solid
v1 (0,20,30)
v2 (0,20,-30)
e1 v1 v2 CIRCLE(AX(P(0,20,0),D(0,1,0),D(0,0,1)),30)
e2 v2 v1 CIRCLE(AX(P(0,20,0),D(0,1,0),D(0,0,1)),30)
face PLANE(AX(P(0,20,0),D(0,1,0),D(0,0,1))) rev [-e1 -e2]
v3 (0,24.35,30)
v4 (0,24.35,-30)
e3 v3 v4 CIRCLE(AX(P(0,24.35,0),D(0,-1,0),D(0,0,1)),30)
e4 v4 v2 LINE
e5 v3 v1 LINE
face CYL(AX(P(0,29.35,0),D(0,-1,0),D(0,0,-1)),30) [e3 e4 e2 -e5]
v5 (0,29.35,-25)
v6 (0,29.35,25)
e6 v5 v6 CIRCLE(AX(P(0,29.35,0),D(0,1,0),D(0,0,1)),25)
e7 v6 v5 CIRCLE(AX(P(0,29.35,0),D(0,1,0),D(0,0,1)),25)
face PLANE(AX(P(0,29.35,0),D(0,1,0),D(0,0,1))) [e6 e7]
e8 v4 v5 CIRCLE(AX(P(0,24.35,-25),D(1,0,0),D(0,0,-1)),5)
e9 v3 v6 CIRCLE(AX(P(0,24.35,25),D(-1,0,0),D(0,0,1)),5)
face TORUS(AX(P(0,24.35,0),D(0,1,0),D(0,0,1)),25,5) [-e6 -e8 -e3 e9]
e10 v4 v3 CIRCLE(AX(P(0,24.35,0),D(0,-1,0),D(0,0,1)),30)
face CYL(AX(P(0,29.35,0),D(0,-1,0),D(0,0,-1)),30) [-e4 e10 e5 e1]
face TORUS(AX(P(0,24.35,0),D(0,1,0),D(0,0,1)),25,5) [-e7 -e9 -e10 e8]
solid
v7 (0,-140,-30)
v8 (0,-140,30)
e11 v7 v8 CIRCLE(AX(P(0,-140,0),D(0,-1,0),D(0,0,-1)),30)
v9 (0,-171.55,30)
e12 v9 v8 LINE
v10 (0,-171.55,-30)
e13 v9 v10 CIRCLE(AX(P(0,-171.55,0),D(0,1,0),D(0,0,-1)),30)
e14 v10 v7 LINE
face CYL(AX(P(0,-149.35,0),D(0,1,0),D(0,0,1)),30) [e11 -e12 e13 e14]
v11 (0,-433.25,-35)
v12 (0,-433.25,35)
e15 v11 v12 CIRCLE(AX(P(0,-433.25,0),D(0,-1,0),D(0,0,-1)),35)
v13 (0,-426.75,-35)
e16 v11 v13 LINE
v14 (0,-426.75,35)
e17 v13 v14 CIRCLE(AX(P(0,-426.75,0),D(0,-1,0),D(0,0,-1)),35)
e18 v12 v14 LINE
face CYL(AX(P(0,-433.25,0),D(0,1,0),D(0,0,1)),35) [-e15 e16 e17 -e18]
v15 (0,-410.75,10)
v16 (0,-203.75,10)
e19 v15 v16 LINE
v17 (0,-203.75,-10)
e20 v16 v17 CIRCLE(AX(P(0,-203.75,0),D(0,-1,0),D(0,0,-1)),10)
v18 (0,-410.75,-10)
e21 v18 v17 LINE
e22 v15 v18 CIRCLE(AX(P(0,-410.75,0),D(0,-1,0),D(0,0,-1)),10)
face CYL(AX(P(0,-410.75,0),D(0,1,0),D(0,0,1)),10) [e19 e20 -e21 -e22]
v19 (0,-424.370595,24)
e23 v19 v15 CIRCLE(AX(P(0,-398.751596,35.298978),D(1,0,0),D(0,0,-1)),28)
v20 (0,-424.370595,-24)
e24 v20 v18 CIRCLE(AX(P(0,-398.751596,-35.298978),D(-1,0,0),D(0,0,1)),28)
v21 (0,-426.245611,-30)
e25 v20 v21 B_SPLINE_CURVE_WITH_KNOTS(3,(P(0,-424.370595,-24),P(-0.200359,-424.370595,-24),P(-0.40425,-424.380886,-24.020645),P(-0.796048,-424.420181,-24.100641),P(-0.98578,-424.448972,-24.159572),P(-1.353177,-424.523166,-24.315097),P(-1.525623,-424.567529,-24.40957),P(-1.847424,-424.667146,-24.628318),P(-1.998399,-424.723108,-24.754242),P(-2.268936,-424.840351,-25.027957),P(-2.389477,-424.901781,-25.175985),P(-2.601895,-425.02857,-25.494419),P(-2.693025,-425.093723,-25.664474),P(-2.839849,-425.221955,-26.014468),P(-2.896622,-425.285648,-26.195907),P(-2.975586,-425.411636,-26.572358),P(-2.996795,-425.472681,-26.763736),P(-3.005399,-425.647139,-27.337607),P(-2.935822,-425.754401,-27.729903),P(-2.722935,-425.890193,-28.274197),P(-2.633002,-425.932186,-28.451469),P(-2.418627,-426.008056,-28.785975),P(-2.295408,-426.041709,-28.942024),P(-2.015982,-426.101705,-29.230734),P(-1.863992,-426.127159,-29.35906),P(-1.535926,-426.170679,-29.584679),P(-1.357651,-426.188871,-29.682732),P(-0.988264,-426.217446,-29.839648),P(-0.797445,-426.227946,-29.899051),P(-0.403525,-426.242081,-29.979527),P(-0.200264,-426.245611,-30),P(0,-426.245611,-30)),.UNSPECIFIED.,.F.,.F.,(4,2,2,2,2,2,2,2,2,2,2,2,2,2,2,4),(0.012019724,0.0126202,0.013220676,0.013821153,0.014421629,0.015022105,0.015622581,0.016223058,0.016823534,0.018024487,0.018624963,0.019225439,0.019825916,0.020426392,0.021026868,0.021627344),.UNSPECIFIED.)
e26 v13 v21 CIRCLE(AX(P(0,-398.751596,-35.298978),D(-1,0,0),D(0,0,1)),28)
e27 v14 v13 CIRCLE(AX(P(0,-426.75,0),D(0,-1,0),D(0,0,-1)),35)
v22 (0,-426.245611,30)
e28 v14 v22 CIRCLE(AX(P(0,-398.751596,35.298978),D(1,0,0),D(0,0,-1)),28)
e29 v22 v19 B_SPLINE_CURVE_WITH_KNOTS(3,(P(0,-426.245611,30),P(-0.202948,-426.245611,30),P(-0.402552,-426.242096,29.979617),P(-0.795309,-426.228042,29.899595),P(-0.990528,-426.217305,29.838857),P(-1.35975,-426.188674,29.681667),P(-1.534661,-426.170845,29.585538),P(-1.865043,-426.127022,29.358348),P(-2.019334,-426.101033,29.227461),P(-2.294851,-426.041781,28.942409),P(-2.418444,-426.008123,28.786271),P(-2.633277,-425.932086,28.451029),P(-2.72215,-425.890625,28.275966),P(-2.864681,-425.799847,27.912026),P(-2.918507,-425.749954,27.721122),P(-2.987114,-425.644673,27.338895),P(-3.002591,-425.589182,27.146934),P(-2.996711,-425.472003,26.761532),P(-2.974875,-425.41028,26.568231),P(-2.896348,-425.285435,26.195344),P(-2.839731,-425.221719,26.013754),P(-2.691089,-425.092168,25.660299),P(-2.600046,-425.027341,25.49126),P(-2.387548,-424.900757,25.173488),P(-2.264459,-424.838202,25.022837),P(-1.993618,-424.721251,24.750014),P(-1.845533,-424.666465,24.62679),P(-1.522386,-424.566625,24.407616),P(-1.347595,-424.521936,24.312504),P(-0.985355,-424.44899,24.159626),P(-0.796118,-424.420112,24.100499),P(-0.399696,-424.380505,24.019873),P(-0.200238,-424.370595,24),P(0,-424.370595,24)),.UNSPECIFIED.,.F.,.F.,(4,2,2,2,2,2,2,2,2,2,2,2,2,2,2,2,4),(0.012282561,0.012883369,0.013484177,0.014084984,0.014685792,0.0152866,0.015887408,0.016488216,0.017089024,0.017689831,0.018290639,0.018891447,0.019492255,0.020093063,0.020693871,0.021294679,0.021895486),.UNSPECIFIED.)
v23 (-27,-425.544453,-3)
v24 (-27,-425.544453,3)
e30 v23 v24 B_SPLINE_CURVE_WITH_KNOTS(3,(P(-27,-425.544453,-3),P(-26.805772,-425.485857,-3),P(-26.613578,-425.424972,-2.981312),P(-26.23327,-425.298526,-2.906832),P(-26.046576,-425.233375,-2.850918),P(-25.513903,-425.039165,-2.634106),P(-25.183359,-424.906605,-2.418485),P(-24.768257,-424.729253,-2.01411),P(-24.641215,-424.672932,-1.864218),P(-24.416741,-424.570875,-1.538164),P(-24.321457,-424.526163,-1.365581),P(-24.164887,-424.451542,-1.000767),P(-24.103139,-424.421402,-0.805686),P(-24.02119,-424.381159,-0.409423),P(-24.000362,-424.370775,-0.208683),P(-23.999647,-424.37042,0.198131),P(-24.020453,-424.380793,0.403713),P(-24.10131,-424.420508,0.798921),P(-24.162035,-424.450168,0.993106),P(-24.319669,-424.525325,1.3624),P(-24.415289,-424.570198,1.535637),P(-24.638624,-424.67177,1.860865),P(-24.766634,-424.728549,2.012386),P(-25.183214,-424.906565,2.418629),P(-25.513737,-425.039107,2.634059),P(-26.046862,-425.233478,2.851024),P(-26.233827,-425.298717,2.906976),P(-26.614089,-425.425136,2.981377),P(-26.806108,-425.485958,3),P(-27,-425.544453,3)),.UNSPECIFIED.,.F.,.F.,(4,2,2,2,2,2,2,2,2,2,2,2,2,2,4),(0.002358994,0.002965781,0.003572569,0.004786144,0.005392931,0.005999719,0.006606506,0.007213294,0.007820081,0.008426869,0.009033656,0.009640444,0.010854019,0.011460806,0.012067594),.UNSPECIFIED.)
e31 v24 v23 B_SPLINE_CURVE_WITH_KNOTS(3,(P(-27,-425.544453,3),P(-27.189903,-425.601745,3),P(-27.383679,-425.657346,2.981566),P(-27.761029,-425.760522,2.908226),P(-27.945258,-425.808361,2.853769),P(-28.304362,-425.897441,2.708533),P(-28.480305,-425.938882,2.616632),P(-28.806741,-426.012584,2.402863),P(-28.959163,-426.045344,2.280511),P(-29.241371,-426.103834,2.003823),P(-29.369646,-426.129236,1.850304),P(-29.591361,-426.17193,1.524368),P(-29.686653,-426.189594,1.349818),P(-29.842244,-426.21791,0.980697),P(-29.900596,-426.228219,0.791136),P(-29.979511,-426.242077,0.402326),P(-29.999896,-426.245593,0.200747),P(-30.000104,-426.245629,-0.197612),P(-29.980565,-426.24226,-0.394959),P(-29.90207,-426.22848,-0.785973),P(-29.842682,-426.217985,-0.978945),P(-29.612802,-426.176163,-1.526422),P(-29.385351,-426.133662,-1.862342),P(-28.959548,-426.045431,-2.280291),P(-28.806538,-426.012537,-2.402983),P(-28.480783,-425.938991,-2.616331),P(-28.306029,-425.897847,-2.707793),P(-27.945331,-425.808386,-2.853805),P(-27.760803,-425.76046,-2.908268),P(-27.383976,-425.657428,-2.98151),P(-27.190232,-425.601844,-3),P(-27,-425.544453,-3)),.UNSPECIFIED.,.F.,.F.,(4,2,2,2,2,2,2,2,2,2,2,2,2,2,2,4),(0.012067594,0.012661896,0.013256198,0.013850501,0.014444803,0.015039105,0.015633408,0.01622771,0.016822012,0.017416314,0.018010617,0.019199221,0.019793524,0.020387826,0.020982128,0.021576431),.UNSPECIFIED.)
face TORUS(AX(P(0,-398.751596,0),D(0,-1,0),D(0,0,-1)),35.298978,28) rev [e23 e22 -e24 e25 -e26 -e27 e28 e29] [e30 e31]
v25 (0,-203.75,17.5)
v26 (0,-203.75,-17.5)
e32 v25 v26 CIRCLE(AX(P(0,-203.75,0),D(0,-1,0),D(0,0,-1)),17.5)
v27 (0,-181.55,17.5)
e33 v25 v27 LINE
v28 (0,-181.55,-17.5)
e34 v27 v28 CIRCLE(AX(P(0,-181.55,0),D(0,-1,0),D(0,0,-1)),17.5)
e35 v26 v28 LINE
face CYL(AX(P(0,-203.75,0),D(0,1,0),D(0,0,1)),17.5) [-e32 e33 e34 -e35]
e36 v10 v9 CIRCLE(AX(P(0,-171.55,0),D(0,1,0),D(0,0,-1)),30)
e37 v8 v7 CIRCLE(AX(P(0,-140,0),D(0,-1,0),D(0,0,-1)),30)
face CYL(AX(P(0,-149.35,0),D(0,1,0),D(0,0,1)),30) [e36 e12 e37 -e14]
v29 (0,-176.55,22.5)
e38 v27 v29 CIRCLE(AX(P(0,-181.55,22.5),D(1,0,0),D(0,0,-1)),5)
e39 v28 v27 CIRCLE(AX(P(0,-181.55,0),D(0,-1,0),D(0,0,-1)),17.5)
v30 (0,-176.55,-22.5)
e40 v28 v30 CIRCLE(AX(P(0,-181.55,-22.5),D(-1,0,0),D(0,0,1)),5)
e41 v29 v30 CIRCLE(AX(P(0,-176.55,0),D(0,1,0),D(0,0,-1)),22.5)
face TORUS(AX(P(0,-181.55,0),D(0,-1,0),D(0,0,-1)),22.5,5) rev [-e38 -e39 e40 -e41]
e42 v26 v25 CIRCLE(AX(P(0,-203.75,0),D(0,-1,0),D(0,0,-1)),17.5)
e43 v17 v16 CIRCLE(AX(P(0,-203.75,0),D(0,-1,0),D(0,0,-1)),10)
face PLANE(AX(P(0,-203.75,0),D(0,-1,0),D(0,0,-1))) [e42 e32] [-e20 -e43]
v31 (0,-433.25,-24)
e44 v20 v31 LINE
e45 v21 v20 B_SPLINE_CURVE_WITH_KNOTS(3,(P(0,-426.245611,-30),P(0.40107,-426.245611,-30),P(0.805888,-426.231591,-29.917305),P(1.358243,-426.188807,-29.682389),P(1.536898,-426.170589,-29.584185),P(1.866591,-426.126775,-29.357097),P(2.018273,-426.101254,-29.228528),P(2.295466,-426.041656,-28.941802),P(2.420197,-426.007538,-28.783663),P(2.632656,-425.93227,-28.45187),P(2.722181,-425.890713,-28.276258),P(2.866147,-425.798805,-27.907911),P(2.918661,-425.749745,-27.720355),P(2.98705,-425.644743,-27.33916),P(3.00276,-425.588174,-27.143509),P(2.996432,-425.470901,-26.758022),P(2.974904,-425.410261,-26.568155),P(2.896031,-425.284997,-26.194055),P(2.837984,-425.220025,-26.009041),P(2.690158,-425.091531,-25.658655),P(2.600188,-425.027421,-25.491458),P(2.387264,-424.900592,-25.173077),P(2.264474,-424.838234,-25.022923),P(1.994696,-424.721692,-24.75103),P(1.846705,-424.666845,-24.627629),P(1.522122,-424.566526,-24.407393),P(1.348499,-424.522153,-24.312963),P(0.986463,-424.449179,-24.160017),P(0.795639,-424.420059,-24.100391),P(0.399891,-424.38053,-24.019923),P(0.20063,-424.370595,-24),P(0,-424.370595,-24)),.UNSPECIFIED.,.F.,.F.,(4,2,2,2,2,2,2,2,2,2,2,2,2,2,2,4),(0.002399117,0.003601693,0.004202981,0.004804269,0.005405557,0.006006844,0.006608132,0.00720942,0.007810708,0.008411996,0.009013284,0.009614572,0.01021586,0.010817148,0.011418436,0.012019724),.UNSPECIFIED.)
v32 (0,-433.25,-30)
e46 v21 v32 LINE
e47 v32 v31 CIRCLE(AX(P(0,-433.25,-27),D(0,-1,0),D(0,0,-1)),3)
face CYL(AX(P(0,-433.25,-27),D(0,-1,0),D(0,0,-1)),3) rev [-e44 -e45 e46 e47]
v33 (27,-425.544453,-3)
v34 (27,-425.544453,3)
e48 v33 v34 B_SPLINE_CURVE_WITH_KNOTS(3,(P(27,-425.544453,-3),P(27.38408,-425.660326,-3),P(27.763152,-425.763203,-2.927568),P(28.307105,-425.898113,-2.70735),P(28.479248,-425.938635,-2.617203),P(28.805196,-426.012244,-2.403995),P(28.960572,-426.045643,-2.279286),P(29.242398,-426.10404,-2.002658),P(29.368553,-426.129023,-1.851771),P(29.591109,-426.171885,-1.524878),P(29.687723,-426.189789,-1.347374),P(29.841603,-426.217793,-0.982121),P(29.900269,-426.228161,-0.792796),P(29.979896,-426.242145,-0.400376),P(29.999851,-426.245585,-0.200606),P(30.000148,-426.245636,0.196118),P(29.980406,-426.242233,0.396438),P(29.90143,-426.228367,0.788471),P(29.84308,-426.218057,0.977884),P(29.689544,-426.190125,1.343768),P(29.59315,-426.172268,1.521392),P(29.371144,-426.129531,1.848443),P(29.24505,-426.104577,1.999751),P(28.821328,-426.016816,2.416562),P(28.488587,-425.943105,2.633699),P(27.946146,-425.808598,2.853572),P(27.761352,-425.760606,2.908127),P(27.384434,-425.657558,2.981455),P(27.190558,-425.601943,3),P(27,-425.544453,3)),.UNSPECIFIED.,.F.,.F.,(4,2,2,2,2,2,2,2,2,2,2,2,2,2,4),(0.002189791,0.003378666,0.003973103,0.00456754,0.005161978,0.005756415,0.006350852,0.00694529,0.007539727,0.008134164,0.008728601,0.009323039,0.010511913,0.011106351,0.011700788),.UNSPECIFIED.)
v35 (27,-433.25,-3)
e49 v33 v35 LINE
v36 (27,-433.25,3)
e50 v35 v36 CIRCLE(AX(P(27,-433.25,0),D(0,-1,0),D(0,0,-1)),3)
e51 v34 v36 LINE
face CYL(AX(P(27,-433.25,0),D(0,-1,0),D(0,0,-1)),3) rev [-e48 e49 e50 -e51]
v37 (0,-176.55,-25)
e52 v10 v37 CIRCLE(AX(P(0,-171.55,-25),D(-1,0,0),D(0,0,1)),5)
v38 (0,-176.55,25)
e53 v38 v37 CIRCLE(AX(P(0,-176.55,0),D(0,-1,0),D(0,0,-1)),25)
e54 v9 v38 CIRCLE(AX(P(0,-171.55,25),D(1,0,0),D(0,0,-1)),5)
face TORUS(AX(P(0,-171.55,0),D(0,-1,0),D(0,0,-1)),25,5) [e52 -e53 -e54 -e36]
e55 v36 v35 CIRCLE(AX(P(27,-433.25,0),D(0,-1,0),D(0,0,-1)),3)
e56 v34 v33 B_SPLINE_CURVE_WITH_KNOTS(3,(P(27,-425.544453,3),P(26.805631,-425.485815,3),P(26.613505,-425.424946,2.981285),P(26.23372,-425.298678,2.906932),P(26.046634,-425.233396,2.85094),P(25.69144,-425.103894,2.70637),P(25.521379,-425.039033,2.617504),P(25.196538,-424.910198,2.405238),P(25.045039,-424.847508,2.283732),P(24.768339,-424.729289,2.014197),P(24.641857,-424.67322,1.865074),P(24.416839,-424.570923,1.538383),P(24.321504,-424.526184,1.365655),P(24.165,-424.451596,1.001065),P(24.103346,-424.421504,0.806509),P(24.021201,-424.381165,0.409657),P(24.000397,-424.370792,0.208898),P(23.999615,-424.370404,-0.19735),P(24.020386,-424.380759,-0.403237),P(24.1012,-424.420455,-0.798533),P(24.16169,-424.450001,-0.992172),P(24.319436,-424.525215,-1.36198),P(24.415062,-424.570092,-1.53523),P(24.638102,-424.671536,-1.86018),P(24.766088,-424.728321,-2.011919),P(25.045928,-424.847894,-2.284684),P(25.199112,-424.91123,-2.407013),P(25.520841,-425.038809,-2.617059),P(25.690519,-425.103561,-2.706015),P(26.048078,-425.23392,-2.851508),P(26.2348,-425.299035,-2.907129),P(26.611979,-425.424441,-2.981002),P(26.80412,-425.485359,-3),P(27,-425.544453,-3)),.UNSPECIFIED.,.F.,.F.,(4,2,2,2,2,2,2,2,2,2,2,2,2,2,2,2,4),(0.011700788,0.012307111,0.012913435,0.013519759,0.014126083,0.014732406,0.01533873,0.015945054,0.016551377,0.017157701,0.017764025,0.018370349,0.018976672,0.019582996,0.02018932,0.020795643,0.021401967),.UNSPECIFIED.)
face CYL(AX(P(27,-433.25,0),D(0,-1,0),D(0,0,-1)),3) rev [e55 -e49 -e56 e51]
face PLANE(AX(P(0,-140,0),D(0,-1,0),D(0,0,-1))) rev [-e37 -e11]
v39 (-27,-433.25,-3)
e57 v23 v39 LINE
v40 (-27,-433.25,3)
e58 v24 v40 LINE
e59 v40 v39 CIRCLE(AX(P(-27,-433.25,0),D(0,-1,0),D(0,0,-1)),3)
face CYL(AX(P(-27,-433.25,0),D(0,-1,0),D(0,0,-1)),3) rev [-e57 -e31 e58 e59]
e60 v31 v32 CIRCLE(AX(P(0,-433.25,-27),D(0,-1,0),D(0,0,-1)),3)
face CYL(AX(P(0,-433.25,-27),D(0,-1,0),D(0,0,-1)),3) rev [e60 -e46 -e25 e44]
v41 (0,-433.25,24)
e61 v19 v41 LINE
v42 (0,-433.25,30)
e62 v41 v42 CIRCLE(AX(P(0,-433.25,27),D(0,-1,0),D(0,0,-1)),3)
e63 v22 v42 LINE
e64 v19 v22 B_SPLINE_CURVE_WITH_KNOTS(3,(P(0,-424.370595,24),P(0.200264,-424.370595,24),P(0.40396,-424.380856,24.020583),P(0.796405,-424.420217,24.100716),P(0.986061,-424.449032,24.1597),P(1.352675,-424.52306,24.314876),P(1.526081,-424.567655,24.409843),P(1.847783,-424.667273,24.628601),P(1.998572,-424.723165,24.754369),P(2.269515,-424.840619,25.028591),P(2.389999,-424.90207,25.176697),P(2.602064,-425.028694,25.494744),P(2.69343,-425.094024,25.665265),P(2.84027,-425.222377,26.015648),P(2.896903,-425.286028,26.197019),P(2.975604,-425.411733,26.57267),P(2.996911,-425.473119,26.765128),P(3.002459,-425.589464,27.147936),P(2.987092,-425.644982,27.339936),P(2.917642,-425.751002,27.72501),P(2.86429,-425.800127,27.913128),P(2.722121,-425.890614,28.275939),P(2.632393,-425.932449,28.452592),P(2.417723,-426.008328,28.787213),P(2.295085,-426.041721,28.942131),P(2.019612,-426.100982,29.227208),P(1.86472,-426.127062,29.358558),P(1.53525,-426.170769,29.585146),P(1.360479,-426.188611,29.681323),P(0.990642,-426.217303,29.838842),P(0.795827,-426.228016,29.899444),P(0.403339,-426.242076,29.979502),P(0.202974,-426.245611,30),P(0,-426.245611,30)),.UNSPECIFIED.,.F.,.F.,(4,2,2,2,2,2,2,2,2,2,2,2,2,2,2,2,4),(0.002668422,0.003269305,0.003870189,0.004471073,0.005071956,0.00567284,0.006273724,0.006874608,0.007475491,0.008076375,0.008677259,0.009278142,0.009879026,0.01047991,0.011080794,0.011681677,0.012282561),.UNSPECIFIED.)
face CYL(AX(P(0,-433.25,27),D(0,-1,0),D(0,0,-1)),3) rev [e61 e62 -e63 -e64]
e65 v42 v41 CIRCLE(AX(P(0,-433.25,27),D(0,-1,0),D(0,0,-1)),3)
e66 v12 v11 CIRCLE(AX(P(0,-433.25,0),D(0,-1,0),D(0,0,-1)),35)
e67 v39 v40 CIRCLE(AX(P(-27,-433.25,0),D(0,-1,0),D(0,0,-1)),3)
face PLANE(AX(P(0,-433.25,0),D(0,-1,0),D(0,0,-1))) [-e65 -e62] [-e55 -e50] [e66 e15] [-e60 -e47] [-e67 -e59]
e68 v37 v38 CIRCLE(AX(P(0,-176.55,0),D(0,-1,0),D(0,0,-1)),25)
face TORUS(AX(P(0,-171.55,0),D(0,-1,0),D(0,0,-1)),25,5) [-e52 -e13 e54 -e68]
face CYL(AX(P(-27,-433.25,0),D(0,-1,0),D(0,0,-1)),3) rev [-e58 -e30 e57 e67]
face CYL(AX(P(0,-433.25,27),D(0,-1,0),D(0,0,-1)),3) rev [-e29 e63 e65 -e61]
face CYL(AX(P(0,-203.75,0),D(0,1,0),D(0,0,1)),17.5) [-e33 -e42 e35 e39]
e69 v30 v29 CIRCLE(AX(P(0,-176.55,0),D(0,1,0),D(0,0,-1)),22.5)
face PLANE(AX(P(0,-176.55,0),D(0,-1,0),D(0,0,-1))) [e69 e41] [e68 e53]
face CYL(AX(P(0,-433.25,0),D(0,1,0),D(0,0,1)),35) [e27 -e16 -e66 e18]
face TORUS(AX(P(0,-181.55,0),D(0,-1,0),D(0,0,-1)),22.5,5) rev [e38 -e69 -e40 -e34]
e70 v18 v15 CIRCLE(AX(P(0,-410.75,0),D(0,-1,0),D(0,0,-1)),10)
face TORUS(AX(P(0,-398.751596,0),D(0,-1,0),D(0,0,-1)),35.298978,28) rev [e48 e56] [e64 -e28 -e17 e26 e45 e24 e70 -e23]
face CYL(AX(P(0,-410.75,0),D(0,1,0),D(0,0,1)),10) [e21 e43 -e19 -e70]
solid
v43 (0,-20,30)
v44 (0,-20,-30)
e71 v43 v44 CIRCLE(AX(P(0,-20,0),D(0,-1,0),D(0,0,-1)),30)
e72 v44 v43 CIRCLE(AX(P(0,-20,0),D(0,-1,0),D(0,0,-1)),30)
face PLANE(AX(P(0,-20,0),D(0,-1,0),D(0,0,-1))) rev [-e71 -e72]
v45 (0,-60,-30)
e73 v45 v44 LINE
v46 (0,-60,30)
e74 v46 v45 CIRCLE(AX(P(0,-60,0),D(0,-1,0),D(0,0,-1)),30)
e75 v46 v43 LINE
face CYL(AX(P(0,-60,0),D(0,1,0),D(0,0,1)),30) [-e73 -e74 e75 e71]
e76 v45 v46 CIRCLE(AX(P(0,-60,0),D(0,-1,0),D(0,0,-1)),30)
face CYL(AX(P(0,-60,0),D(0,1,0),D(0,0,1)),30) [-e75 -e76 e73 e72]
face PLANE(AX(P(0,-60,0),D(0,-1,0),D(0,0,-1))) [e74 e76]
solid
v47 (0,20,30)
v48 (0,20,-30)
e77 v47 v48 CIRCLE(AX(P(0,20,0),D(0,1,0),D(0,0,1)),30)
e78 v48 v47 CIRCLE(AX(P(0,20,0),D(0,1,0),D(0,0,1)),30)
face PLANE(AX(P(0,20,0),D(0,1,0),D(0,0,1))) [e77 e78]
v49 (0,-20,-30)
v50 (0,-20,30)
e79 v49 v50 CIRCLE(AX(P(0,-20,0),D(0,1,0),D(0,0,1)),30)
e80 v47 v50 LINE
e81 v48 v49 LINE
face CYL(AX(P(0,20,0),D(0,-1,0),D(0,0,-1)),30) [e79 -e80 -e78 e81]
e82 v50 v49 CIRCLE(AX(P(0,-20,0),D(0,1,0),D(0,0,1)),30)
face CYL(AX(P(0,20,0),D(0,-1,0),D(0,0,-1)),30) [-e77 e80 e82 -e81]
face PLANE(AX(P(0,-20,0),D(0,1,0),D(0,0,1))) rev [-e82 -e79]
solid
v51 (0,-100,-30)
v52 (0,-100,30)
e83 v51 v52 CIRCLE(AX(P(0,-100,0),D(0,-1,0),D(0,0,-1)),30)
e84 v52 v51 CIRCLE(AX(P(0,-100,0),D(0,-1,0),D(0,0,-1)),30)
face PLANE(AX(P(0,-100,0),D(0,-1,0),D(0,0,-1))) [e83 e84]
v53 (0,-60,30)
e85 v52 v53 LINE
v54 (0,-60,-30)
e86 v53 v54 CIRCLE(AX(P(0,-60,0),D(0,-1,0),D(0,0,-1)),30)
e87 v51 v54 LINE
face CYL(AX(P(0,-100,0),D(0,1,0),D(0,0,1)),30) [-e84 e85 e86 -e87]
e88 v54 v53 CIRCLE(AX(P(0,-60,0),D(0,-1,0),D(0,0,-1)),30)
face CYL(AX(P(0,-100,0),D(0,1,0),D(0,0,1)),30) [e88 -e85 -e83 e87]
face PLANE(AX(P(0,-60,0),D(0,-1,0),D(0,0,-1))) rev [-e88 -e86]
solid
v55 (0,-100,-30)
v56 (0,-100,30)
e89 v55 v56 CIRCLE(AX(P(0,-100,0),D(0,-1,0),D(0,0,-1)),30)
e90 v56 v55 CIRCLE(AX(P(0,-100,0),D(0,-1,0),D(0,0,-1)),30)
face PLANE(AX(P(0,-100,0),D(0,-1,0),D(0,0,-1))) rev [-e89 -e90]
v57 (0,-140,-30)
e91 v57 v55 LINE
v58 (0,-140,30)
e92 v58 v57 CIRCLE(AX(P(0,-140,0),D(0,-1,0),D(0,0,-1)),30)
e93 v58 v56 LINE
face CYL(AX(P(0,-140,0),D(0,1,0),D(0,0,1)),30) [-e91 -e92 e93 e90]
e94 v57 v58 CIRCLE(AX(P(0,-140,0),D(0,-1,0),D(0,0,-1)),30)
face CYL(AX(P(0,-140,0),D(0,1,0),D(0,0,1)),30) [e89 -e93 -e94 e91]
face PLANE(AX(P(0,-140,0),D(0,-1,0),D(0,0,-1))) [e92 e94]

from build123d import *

# Parameters (mm, degrees)
SKETCH_1_R                     = 30
EXTRUDE_1_DEPTH                = 20
SKETCH_2_R                     = 30
EXTRUDE_2_DEPTH                = 40
SKETCH_3_R                     = 30
EXTRUDE_3_DEPTH                = 40
SKETCH_4_R                     = 30
EXTRUDE_4_DEPTH                = 40
SKETCH_5_R                     = 30
EXTRUDE_5_DEPTH                = 9.35
SKETCH_6_R                     = 30
EXTRUDE_6_DEPTH                = 9.35
SKETCH_7_R                     = 30
EXTRUDE_7_DEPTH                = 27.2
SKETCH_8_R                     = 17.5
EXTRUDE_8_DEPTH                = 27.2
FILLET_1_R                     = 5
SKETCH_9_R                     = 10
EXTRUDE_9_DEPTH                = 207
FILLET_2_R                     = 5
FILLET_3_R                     = 5
SKETCH_10_R                    = 35
EXTRUDE_10_DEPTH               = 22.5
HOLE_WIZARD_6_0_6_2_AT_2_COUNT = 2
HOLE_WIZARD_6_0_6_2_AT_2_PITCH = 54
HOLE_WIZARD_6_0_6_2_AT_3_COUNT = 2
HOLE_WIZARD_6_0_6_2_AT_3_PITCH = 38.183766184
HOLE_WIZARD_6_0_6_2_AT_4_COUNT = 2
HOLE_WIZARD_6_0_6_2_AT_4_PITCH = 38.183766184


with BuildPart() as part:
    # 草图1 → 凸台-拉伸1 (new, symmetric)
    with BuildSketch(Plane(origin=(0, 0, 0), x_dir=(1, 0, 0), z_dir=(0, 1, 0))):
        with Locations(Location((0, 0, 0), (0, 0, 270))):
            Circle(SKETCH_1_R)
    extrude(amount=EXTRUDE_1_DEPTH, both=True)


with BuildPart() as body_2:
    # 草图2 → 凸台-拉伸2 (new body)
    with BuildSketch(Plane.XZ.offset(20)):
        with Locations(Location((0, 0, 0), (0, 0, 270))):
            Circle(SKETCH_2_R)
    extrude(amount=EXTRUDE_2_DEPTH)


with BuildPart() as body_3:
    # 草图3 → 凸台-拉伸3 (new body)
    with BuildSketch(Plane.XZ.offset(60)):
        with Locations(Location((0, 0, 0), (0, 0, 270))):
            Circle(SKETCH_3_R)
    extrude(amount=EXTRUDE_3_DEPTH)


with BuildPart() as body_4:
    # 草图4 → 凸台-拉伸4 (new body)
    with BuildSketch(Plane.XZ.offset(100)):
        with Locations(Location((0, 0, 0), (0, 0, 270))):
            Circle(SKETCH_4_R)
    extrude(amount=EXTRUDE_4_DEPTH)


with BuildPart() as body_5:
    # 草图5 → 凸台-拉伸5 (new body)
    with BuildSketch(Plane(origin=(0, 20, 0), x_dir=(1, 0, 0), z_dir=(0, 1, 0))):
        with Locations(Location((0, 0, 0), (0, 0, 270))):
            Circle(SKETCH_5_R)
    extrude(amount=EXTRUDE_5_DEPTH)

    # 圆角1
    fillet_1_edges = [body_5.edges().sort_by_distance(p)[0] for p in [
        (0, 29.35, -30),
    ]]
    fillet(fillet_1_edges, radius=FILLET_1_R)


with BuildPart() as body_6:
    # 草图6 → 凸台-拉伸6 (new body)
    with BuildSketch(Plane.XZ.offset(140)):
        with Locations(Location((0, 0, 0), (0, 0, 270))):
            Circle(SKETCH_6_R)
    extrude(amount=EXTRUDE_6_DEPTH)

    # 草图7 → 凸台-拉伸7 (add)
    with BuildSketch(Plane.XZ.offset(149.35)):
        with Locations(Location((0, 0, 0), (0, 0, 270))):
            Circle(SKETCH_7_R)
    extrude(amount=EXTRUDE_7_DEPTH)

    # 草图8 → 凸台-拉伸8 (add)
    with BuildSketch(Plane.XZ.offset(176.55)):
        with Locations(Location((0, 0, 0), (0, 0, 270))):
            Circle(SKETCH_8_R)
    extrude(amount=EXTRUDE_8_DEPTH)

    # 草图9 → 凸台-拉伸9 (add)
    with BuildSketch(Plane.XZ.offset(203.75)):
        with Locations(Location((0, 0, 0), (0, 0, 270))):
            Circle(SKETCH_9_R)
    extrude(amount=EXTRUDE_9_DEPTH)

    # 圆角2
    fillet_2_edges = [body_6.edges().sort_by_distance(p)[0] for p in [
        (0, -176.55, 17.5),
    ]]
    fillet(fillet_2_edges, radius=FILLET_2_R)

    # 圆角3
    fillet_3_edges = [body_6.edges().sort_by_distance(p)[0] for p in [
        (0, -176.55, 30),
    ]]
    fillet(fillet_3_edges, radius=FILLET_3_R)

    # 草图10 → 凸台-拉伸10 (add)
    with BuildSketch(Plane.XZ.offset(410.75)):
        with Locations(Location((0, 0, 0), (0, 0, 90))):
            Circle(SKETCH_10_R)
    extrude(amount=EXTRUDE_10_DEPTH)

    # 草图11 → 切除-旋转1 (revolve, cut)
    with BuildSketch(Plane(origin=(0, 0, 0), x_dir=(0, 0, -1), z_dir=(1, 0, 0))):
        with BuildLine():
            Line((10, -410.75), (35, -410.75))
            Line((35, -410.75), (35, -426.75))
            ThreePointArc((35, -426.75), (20.205474893, -422.33519548), (10, -410.75))
        make_face()
    revolve(axis=Axis((0, -433.25, 0), (0, 1, 0)), mode=Mode.SUBTRACT)

    # 草图15 → Ø6.0 (6) 直径孔2 (revolve, cut)
    with BuildSketch(Plane(origin=(0, -433.25, 27), x_dir=(0, 0, -1), z_dir=(1, 0, 0))):
        Polygon((0, 0), (0, 36.802581857), (3, 35), (3, 0), align=None)
    hole_wizard_6_0_6_2 = revolve(axis=Axis((0, -439.6, 27), (0, 1, 0)), mode=Mode.SUBTRACT)

    # Ø6.0 (6) 直径孔2 at 2: Ø6.0 (6) 直径孔2 ×2
    with Locations(*[(0, 0, -i * HOLE_WIZARD_6_0_6_2_AT_2_PITCH) for i in range(1, HOLE_WIZARD_6_0_6_2_AT_2_COUNT)]):
        add(hole_wizard_6_0_6_2, mode=Mode.SUBTRACT)

    # Ø6.0 (6) 直径孔2 at 3: Ø6.0 (6) 直径孔2 ×2
    with Locations(*[Vector(-0.7071067811865476, 0, -0.7071067811865476) * (i * HOLE_WIZARD_6_0_6_2_AT_3_PITCH) for i in range(1, HOLE_WIZARD_6_0_6_2_AT_3_COUNT)]):
        add(hole_wizard_6_0_6_2, mode=Mode.SUBTRACT)

    # Ø6.0 (6) 直径孔2 at 4: Ø6.0 (6) 直径孔2 ×2
    with Locations(*[Vector(0.7071067811865476, 0, -0.7071067811865476) * (i * HOLE_WIZARD_6_0_6_2_AT_4_PITCH) for i in range(1, HOLE_WIZARD_6_0_6_2_AT_4_COUNT)]):
        add(hole_wizard_6_0_6_2, mode=Mode.SUBTRACT)


solid = Compound([part.part, body_2.part, body_3.part, body_4.part, body_5.part, body_6.part])
